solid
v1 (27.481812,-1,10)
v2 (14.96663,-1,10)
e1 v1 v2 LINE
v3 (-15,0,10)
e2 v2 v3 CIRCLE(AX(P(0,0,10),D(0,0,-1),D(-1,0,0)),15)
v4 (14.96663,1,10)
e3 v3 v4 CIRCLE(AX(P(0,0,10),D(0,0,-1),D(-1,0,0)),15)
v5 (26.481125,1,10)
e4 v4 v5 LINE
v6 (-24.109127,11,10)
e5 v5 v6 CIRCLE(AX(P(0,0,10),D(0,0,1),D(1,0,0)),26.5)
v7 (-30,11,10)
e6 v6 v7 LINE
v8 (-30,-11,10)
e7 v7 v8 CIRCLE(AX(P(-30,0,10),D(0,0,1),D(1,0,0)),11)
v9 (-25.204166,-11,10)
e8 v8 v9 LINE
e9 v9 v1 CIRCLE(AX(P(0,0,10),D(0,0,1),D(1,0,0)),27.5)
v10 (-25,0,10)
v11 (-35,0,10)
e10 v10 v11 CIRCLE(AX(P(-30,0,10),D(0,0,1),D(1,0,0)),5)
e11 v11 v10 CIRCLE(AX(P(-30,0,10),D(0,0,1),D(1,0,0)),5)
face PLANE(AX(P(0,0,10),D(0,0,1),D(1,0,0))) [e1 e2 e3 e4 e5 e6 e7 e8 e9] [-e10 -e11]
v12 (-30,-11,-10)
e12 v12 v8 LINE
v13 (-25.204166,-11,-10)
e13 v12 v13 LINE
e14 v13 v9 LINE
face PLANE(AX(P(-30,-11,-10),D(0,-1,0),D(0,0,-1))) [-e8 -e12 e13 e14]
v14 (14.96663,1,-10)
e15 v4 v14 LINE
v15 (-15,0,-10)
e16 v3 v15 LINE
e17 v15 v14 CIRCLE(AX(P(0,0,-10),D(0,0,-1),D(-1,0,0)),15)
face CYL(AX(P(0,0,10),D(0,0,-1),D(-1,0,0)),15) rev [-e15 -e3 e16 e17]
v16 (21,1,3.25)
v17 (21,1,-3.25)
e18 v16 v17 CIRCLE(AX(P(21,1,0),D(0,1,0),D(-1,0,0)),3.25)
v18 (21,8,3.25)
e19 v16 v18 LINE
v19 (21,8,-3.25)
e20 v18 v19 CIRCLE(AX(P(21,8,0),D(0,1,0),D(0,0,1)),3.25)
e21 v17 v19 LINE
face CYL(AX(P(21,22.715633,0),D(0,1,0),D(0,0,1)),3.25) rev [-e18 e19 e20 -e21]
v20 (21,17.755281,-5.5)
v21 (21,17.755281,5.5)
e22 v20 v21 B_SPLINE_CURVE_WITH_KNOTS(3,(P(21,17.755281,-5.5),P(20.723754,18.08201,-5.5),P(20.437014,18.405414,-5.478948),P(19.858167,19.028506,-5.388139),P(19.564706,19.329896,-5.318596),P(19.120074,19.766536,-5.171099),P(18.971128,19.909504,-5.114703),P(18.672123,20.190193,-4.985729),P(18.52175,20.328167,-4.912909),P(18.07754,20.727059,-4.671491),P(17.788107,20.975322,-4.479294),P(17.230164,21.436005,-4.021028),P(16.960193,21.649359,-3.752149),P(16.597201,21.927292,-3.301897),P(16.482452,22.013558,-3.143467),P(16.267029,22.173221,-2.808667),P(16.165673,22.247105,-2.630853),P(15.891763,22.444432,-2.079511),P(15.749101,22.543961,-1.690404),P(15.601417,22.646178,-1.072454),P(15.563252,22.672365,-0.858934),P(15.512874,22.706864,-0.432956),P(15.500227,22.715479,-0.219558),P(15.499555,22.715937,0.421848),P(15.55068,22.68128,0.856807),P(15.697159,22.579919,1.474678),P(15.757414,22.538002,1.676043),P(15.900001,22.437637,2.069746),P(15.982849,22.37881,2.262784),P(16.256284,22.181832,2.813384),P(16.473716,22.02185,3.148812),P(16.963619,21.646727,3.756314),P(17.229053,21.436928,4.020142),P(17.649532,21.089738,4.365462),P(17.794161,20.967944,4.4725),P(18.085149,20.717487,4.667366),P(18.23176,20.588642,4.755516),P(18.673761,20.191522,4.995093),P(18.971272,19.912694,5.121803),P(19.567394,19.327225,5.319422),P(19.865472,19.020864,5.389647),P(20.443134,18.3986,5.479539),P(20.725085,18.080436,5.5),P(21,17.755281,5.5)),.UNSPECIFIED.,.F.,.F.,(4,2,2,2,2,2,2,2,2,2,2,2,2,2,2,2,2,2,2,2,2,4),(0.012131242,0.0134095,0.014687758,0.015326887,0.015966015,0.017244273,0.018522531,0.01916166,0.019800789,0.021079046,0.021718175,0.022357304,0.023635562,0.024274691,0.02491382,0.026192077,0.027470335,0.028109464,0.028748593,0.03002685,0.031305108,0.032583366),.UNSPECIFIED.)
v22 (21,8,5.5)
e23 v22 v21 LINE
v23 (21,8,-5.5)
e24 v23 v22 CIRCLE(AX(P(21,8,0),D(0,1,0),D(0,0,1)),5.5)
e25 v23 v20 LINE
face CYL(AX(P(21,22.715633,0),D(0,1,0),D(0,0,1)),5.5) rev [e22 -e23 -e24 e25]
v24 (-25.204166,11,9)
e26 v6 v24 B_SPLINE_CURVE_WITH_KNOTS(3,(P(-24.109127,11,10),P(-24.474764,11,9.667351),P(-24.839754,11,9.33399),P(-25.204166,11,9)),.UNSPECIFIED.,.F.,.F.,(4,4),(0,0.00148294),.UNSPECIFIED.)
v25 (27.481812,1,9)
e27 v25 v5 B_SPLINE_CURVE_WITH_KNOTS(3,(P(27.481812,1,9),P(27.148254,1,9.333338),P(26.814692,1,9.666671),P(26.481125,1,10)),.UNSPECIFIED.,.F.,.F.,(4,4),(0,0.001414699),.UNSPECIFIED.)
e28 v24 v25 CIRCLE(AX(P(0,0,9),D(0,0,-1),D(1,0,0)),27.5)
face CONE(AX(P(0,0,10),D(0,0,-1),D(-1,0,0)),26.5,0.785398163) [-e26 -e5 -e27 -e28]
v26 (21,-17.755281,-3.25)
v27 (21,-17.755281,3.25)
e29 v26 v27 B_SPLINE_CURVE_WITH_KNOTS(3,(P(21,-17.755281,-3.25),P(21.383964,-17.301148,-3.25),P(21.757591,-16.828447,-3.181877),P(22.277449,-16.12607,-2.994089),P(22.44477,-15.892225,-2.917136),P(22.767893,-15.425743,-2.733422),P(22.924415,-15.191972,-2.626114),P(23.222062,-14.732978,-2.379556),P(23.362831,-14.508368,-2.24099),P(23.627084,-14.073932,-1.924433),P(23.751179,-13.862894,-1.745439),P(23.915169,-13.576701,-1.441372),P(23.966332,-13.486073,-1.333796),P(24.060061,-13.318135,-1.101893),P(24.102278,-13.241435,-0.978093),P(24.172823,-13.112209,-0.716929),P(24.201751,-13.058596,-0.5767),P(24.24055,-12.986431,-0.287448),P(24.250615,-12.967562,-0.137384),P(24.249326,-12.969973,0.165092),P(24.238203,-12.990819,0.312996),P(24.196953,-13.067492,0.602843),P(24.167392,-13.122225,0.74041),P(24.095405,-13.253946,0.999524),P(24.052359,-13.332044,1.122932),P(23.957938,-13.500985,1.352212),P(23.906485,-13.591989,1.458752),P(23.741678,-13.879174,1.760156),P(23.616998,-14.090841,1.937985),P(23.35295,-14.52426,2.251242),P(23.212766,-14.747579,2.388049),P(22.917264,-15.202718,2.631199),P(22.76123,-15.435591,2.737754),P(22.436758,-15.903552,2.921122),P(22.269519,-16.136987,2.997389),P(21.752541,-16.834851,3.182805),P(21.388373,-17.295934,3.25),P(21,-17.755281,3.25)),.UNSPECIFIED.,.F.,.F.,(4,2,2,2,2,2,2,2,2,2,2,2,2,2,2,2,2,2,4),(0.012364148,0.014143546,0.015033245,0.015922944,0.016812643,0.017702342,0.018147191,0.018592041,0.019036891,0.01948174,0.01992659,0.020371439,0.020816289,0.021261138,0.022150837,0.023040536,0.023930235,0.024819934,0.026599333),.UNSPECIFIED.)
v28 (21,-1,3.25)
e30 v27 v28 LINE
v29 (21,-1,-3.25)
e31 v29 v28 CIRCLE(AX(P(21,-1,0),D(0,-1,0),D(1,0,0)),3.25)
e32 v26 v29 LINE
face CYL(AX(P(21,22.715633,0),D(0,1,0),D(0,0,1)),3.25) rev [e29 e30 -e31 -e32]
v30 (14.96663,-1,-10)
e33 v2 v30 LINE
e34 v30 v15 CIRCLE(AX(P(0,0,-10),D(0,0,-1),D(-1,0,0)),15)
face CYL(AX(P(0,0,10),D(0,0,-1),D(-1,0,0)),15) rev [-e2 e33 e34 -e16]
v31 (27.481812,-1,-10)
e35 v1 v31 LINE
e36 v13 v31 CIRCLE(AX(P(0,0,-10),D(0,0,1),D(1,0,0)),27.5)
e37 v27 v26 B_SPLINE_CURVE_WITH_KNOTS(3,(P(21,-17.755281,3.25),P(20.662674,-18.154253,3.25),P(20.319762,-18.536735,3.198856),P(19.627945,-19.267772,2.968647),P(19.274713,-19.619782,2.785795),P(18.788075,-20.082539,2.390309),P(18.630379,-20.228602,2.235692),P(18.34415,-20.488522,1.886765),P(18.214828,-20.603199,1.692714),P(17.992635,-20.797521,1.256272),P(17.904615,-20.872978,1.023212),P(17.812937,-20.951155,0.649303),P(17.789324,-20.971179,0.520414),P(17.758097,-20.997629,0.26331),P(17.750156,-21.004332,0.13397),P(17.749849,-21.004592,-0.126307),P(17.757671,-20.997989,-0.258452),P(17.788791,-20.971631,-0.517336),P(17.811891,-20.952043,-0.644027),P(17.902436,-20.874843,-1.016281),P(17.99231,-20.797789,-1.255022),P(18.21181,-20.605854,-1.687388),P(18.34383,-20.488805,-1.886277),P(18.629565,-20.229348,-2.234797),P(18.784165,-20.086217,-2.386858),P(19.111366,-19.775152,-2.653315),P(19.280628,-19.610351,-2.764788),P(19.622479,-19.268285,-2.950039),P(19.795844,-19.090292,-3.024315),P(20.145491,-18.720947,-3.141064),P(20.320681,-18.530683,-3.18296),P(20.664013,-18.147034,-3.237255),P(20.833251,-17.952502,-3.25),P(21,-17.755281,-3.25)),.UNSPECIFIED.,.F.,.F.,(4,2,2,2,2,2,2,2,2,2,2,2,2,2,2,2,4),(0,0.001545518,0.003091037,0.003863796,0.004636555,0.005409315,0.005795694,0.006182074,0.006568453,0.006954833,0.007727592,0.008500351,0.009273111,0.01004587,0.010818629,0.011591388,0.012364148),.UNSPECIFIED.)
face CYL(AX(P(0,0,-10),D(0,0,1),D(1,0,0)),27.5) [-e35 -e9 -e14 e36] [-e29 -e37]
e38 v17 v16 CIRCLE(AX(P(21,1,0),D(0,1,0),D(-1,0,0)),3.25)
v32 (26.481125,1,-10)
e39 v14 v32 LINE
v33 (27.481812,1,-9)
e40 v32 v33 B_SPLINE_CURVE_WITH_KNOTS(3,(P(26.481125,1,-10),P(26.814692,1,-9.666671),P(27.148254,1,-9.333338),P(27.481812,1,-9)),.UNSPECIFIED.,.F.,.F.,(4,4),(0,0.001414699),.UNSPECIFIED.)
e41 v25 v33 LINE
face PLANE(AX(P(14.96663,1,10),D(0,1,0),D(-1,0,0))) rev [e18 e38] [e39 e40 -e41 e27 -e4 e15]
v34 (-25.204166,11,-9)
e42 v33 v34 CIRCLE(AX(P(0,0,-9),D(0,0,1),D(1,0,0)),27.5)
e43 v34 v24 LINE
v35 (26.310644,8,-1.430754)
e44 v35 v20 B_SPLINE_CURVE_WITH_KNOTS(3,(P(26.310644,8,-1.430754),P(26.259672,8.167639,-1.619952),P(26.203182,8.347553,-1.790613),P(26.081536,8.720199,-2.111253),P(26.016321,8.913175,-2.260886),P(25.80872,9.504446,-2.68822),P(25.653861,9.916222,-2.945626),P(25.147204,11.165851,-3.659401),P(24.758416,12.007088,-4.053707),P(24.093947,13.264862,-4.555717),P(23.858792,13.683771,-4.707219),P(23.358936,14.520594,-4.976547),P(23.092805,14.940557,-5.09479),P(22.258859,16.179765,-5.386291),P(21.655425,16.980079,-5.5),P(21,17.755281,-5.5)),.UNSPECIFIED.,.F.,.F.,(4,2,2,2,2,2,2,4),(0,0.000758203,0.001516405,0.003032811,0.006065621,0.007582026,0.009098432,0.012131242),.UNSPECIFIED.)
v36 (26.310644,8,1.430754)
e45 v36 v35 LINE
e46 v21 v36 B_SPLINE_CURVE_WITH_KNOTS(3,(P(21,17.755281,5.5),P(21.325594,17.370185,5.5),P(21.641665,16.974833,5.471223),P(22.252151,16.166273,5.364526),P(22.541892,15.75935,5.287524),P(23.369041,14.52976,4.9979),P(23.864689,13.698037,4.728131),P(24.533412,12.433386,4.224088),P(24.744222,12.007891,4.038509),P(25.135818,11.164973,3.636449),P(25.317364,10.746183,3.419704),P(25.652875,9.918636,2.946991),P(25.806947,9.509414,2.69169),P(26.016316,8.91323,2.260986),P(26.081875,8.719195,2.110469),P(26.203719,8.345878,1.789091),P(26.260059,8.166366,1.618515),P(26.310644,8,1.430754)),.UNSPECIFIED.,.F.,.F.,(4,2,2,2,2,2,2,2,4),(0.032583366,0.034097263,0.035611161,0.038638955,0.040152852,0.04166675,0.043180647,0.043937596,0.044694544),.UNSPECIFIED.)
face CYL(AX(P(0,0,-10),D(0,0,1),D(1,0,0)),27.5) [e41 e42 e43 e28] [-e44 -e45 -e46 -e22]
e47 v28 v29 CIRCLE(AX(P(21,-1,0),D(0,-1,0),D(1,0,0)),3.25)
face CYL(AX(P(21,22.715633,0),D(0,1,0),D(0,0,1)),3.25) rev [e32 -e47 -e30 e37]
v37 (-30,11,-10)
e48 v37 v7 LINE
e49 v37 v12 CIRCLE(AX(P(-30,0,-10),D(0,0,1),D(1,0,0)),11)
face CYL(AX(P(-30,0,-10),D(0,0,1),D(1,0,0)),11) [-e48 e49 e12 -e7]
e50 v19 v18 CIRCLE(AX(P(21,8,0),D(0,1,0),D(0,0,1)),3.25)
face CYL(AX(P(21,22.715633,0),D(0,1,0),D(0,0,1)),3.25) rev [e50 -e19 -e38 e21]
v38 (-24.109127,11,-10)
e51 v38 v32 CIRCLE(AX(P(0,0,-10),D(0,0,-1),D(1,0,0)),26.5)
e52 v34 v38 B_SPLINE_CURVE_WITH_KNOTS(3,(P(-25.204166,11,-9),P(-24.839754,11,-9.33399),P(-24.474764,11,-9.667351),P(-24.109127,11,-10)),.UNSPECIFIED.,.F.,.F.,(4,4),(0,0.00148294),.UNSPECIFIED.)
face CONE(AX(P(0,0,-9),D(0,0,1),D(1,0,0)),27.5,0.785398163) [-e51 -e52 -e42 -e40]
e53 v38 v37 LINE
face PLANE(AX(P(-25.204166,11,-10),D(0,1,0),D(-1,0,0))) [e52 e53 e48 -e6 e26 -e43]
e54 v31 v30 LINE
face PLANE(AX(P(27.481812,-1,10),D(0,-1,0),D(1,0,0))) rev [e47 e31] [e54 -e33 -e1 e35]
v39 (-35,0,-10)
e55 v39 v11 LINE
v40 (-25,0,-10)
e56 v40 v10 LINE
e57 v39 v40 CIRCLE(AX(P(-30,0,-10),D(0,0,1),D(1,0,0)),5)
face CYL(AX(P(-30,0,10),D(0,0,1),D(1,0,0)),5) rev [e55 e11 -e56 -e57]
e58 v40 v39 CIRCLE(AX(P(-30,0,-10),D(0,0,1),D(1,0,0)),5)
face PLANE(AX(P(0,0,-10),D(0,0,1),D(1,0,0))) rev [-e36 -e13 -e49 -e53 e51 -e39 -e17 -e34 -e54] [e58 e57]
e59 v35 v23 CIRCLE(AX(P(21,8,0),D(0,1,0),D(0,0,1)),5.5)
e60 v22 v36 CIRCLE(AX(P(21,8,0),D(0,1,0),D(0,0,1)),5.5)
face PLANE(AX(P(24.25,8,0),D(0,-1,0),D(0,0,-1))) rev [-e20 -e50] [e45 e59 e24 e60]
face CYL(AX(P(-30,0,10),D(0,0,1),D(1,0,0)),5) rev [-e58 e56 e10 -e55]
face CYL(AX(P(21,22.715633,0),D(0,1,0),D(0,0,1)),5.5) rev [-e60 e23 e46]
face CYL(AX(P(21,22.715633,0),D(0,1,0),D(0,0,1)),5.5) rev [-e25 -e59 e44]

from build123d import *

# Parameters (mm, degrees)
EXTRUDE_1_DEPTH              = 20
CUT_EXTRUDE_1_DEPTH          = 54.265842714
SKETCH_3_W                   = 15
SKETCH_3_H                   = 20
HOLE_WIZARD_10_0_10_1_D      = 10
SKETCH_6_W                   = 2.5
SKETCH_6_H                   = 26.5
HOLE_WIZARD_M6_1_D           = 6.5
HOLE_WIZARD_M6_1_DEPTH       = 50.215633411
HOLE_WIZARD_M6_1_CBORE_D     = 11
HOLE_WIZARD_M6_1_CBORE_DEPTH = 14.715633411
CHAMFER_1_SIZE               = 1


with BuildPart() as part:
    # 草图1 → 凸台-拉伸1 (new body)
    with BuildSketch(Plane.XY.offset(10)):
        with BuildLine():
            Line((-25.204166322, 11), (-30, 11))
            ThreePointArc((-30, 11), (-41, 0), (-30, -11))
            Line((-30, -11), (-25.204166322, -11))
            ThreePointArc((-25.204166322, -11), (27.5, 0), (-25.204166322, 11))
        make_face()
    extrude(amount=-EXTRUDE_1_DEPTH)

    # 草图2 → 切除-拉伸1 (cut, through all)
    with BuildSketch(Plane(origin=(0, 0, -10), x_dir=(-1, 0, 0), z_dir=(0, 0, -1))):
        with BuildLine():
            Line((-27.481812167, -1), (-14.966629547, -1))
            ThreePointArc((-14.966629547, -1), (-15, 0), (-14.966629547, 1))
            Line((-14.966629547, 1), (-27.481812167, 1))
            ThreePointArc((-27.481812167, 1), (-27.5, 0), (-27.481812167, -1))
        make_face()
    extrude(amount=-CUT_EXTRUDE_1_DEPTH, mode=Mode.SUBTRACT)

    # 草图3 → 切除-旋转1 (revolve, cut)
    with BuildSketch(Plane.XZ):
        with Locations((7.5, 0)):
            Rectangle(SKETCH_3_W, SKETCH_3_H)
    revolve(axis=Axis((0, 0, 10), (0, 0, -1)), mode=Mode.SUBTRACT)

    # Ø10.0 (10) 直径孔1 (through all)
    with Locations(Plane.XY.offset(10)):
        with Locations((-30, 0)):
            Hole(HOLE_WIZARD_10_0_10_1_D / 2)

    # 草图6 → Ø5.0 (5) 直径孔1 (revolve, cut)
    with BuildSketch(Plane(origin=(21, -1, 0), x_dir=(0, 0, 1), z_dir=(1, 0, 0))):
        with Locations((1.25, 13.25)):
            Rectangle(SKETCH_6_W, SKETCH_6_H)
    revolve(axis=Axis((21, 5.35, 0), (0, -1, 0)), mode=Mode.SUBTRACT)

    # M6 六角头螺栓的柱形沉头孔1
    with Locations(Plane(origin=(0, 22.715633411, 0), x_dir=(1, 0, 0), z_dir=(0, 1, 0))):
        with Locations((21, 0)):
            CounterBoreHole(HOLE_WIZARD_M6_1_D / 2, HOLE_WIZARD_M6_1_CBORE_D / 2, HOLE_WIZARD_M6_1_CBORE_DEPTH, depth=HOLE_WIZARD_M6_1_DEPTH)

    # 倒角1
    chamfer_1_edges = [part.edges().sort_by_distance(p)[0] for p in [
        (5.128052033, 27.017643908, -10),
        (5.128052033, 27.017643908, 10),
    ]]
    chamfer(chamfer_1_edges, length=CHAMFER_1_SIZE)


solid = part.part
